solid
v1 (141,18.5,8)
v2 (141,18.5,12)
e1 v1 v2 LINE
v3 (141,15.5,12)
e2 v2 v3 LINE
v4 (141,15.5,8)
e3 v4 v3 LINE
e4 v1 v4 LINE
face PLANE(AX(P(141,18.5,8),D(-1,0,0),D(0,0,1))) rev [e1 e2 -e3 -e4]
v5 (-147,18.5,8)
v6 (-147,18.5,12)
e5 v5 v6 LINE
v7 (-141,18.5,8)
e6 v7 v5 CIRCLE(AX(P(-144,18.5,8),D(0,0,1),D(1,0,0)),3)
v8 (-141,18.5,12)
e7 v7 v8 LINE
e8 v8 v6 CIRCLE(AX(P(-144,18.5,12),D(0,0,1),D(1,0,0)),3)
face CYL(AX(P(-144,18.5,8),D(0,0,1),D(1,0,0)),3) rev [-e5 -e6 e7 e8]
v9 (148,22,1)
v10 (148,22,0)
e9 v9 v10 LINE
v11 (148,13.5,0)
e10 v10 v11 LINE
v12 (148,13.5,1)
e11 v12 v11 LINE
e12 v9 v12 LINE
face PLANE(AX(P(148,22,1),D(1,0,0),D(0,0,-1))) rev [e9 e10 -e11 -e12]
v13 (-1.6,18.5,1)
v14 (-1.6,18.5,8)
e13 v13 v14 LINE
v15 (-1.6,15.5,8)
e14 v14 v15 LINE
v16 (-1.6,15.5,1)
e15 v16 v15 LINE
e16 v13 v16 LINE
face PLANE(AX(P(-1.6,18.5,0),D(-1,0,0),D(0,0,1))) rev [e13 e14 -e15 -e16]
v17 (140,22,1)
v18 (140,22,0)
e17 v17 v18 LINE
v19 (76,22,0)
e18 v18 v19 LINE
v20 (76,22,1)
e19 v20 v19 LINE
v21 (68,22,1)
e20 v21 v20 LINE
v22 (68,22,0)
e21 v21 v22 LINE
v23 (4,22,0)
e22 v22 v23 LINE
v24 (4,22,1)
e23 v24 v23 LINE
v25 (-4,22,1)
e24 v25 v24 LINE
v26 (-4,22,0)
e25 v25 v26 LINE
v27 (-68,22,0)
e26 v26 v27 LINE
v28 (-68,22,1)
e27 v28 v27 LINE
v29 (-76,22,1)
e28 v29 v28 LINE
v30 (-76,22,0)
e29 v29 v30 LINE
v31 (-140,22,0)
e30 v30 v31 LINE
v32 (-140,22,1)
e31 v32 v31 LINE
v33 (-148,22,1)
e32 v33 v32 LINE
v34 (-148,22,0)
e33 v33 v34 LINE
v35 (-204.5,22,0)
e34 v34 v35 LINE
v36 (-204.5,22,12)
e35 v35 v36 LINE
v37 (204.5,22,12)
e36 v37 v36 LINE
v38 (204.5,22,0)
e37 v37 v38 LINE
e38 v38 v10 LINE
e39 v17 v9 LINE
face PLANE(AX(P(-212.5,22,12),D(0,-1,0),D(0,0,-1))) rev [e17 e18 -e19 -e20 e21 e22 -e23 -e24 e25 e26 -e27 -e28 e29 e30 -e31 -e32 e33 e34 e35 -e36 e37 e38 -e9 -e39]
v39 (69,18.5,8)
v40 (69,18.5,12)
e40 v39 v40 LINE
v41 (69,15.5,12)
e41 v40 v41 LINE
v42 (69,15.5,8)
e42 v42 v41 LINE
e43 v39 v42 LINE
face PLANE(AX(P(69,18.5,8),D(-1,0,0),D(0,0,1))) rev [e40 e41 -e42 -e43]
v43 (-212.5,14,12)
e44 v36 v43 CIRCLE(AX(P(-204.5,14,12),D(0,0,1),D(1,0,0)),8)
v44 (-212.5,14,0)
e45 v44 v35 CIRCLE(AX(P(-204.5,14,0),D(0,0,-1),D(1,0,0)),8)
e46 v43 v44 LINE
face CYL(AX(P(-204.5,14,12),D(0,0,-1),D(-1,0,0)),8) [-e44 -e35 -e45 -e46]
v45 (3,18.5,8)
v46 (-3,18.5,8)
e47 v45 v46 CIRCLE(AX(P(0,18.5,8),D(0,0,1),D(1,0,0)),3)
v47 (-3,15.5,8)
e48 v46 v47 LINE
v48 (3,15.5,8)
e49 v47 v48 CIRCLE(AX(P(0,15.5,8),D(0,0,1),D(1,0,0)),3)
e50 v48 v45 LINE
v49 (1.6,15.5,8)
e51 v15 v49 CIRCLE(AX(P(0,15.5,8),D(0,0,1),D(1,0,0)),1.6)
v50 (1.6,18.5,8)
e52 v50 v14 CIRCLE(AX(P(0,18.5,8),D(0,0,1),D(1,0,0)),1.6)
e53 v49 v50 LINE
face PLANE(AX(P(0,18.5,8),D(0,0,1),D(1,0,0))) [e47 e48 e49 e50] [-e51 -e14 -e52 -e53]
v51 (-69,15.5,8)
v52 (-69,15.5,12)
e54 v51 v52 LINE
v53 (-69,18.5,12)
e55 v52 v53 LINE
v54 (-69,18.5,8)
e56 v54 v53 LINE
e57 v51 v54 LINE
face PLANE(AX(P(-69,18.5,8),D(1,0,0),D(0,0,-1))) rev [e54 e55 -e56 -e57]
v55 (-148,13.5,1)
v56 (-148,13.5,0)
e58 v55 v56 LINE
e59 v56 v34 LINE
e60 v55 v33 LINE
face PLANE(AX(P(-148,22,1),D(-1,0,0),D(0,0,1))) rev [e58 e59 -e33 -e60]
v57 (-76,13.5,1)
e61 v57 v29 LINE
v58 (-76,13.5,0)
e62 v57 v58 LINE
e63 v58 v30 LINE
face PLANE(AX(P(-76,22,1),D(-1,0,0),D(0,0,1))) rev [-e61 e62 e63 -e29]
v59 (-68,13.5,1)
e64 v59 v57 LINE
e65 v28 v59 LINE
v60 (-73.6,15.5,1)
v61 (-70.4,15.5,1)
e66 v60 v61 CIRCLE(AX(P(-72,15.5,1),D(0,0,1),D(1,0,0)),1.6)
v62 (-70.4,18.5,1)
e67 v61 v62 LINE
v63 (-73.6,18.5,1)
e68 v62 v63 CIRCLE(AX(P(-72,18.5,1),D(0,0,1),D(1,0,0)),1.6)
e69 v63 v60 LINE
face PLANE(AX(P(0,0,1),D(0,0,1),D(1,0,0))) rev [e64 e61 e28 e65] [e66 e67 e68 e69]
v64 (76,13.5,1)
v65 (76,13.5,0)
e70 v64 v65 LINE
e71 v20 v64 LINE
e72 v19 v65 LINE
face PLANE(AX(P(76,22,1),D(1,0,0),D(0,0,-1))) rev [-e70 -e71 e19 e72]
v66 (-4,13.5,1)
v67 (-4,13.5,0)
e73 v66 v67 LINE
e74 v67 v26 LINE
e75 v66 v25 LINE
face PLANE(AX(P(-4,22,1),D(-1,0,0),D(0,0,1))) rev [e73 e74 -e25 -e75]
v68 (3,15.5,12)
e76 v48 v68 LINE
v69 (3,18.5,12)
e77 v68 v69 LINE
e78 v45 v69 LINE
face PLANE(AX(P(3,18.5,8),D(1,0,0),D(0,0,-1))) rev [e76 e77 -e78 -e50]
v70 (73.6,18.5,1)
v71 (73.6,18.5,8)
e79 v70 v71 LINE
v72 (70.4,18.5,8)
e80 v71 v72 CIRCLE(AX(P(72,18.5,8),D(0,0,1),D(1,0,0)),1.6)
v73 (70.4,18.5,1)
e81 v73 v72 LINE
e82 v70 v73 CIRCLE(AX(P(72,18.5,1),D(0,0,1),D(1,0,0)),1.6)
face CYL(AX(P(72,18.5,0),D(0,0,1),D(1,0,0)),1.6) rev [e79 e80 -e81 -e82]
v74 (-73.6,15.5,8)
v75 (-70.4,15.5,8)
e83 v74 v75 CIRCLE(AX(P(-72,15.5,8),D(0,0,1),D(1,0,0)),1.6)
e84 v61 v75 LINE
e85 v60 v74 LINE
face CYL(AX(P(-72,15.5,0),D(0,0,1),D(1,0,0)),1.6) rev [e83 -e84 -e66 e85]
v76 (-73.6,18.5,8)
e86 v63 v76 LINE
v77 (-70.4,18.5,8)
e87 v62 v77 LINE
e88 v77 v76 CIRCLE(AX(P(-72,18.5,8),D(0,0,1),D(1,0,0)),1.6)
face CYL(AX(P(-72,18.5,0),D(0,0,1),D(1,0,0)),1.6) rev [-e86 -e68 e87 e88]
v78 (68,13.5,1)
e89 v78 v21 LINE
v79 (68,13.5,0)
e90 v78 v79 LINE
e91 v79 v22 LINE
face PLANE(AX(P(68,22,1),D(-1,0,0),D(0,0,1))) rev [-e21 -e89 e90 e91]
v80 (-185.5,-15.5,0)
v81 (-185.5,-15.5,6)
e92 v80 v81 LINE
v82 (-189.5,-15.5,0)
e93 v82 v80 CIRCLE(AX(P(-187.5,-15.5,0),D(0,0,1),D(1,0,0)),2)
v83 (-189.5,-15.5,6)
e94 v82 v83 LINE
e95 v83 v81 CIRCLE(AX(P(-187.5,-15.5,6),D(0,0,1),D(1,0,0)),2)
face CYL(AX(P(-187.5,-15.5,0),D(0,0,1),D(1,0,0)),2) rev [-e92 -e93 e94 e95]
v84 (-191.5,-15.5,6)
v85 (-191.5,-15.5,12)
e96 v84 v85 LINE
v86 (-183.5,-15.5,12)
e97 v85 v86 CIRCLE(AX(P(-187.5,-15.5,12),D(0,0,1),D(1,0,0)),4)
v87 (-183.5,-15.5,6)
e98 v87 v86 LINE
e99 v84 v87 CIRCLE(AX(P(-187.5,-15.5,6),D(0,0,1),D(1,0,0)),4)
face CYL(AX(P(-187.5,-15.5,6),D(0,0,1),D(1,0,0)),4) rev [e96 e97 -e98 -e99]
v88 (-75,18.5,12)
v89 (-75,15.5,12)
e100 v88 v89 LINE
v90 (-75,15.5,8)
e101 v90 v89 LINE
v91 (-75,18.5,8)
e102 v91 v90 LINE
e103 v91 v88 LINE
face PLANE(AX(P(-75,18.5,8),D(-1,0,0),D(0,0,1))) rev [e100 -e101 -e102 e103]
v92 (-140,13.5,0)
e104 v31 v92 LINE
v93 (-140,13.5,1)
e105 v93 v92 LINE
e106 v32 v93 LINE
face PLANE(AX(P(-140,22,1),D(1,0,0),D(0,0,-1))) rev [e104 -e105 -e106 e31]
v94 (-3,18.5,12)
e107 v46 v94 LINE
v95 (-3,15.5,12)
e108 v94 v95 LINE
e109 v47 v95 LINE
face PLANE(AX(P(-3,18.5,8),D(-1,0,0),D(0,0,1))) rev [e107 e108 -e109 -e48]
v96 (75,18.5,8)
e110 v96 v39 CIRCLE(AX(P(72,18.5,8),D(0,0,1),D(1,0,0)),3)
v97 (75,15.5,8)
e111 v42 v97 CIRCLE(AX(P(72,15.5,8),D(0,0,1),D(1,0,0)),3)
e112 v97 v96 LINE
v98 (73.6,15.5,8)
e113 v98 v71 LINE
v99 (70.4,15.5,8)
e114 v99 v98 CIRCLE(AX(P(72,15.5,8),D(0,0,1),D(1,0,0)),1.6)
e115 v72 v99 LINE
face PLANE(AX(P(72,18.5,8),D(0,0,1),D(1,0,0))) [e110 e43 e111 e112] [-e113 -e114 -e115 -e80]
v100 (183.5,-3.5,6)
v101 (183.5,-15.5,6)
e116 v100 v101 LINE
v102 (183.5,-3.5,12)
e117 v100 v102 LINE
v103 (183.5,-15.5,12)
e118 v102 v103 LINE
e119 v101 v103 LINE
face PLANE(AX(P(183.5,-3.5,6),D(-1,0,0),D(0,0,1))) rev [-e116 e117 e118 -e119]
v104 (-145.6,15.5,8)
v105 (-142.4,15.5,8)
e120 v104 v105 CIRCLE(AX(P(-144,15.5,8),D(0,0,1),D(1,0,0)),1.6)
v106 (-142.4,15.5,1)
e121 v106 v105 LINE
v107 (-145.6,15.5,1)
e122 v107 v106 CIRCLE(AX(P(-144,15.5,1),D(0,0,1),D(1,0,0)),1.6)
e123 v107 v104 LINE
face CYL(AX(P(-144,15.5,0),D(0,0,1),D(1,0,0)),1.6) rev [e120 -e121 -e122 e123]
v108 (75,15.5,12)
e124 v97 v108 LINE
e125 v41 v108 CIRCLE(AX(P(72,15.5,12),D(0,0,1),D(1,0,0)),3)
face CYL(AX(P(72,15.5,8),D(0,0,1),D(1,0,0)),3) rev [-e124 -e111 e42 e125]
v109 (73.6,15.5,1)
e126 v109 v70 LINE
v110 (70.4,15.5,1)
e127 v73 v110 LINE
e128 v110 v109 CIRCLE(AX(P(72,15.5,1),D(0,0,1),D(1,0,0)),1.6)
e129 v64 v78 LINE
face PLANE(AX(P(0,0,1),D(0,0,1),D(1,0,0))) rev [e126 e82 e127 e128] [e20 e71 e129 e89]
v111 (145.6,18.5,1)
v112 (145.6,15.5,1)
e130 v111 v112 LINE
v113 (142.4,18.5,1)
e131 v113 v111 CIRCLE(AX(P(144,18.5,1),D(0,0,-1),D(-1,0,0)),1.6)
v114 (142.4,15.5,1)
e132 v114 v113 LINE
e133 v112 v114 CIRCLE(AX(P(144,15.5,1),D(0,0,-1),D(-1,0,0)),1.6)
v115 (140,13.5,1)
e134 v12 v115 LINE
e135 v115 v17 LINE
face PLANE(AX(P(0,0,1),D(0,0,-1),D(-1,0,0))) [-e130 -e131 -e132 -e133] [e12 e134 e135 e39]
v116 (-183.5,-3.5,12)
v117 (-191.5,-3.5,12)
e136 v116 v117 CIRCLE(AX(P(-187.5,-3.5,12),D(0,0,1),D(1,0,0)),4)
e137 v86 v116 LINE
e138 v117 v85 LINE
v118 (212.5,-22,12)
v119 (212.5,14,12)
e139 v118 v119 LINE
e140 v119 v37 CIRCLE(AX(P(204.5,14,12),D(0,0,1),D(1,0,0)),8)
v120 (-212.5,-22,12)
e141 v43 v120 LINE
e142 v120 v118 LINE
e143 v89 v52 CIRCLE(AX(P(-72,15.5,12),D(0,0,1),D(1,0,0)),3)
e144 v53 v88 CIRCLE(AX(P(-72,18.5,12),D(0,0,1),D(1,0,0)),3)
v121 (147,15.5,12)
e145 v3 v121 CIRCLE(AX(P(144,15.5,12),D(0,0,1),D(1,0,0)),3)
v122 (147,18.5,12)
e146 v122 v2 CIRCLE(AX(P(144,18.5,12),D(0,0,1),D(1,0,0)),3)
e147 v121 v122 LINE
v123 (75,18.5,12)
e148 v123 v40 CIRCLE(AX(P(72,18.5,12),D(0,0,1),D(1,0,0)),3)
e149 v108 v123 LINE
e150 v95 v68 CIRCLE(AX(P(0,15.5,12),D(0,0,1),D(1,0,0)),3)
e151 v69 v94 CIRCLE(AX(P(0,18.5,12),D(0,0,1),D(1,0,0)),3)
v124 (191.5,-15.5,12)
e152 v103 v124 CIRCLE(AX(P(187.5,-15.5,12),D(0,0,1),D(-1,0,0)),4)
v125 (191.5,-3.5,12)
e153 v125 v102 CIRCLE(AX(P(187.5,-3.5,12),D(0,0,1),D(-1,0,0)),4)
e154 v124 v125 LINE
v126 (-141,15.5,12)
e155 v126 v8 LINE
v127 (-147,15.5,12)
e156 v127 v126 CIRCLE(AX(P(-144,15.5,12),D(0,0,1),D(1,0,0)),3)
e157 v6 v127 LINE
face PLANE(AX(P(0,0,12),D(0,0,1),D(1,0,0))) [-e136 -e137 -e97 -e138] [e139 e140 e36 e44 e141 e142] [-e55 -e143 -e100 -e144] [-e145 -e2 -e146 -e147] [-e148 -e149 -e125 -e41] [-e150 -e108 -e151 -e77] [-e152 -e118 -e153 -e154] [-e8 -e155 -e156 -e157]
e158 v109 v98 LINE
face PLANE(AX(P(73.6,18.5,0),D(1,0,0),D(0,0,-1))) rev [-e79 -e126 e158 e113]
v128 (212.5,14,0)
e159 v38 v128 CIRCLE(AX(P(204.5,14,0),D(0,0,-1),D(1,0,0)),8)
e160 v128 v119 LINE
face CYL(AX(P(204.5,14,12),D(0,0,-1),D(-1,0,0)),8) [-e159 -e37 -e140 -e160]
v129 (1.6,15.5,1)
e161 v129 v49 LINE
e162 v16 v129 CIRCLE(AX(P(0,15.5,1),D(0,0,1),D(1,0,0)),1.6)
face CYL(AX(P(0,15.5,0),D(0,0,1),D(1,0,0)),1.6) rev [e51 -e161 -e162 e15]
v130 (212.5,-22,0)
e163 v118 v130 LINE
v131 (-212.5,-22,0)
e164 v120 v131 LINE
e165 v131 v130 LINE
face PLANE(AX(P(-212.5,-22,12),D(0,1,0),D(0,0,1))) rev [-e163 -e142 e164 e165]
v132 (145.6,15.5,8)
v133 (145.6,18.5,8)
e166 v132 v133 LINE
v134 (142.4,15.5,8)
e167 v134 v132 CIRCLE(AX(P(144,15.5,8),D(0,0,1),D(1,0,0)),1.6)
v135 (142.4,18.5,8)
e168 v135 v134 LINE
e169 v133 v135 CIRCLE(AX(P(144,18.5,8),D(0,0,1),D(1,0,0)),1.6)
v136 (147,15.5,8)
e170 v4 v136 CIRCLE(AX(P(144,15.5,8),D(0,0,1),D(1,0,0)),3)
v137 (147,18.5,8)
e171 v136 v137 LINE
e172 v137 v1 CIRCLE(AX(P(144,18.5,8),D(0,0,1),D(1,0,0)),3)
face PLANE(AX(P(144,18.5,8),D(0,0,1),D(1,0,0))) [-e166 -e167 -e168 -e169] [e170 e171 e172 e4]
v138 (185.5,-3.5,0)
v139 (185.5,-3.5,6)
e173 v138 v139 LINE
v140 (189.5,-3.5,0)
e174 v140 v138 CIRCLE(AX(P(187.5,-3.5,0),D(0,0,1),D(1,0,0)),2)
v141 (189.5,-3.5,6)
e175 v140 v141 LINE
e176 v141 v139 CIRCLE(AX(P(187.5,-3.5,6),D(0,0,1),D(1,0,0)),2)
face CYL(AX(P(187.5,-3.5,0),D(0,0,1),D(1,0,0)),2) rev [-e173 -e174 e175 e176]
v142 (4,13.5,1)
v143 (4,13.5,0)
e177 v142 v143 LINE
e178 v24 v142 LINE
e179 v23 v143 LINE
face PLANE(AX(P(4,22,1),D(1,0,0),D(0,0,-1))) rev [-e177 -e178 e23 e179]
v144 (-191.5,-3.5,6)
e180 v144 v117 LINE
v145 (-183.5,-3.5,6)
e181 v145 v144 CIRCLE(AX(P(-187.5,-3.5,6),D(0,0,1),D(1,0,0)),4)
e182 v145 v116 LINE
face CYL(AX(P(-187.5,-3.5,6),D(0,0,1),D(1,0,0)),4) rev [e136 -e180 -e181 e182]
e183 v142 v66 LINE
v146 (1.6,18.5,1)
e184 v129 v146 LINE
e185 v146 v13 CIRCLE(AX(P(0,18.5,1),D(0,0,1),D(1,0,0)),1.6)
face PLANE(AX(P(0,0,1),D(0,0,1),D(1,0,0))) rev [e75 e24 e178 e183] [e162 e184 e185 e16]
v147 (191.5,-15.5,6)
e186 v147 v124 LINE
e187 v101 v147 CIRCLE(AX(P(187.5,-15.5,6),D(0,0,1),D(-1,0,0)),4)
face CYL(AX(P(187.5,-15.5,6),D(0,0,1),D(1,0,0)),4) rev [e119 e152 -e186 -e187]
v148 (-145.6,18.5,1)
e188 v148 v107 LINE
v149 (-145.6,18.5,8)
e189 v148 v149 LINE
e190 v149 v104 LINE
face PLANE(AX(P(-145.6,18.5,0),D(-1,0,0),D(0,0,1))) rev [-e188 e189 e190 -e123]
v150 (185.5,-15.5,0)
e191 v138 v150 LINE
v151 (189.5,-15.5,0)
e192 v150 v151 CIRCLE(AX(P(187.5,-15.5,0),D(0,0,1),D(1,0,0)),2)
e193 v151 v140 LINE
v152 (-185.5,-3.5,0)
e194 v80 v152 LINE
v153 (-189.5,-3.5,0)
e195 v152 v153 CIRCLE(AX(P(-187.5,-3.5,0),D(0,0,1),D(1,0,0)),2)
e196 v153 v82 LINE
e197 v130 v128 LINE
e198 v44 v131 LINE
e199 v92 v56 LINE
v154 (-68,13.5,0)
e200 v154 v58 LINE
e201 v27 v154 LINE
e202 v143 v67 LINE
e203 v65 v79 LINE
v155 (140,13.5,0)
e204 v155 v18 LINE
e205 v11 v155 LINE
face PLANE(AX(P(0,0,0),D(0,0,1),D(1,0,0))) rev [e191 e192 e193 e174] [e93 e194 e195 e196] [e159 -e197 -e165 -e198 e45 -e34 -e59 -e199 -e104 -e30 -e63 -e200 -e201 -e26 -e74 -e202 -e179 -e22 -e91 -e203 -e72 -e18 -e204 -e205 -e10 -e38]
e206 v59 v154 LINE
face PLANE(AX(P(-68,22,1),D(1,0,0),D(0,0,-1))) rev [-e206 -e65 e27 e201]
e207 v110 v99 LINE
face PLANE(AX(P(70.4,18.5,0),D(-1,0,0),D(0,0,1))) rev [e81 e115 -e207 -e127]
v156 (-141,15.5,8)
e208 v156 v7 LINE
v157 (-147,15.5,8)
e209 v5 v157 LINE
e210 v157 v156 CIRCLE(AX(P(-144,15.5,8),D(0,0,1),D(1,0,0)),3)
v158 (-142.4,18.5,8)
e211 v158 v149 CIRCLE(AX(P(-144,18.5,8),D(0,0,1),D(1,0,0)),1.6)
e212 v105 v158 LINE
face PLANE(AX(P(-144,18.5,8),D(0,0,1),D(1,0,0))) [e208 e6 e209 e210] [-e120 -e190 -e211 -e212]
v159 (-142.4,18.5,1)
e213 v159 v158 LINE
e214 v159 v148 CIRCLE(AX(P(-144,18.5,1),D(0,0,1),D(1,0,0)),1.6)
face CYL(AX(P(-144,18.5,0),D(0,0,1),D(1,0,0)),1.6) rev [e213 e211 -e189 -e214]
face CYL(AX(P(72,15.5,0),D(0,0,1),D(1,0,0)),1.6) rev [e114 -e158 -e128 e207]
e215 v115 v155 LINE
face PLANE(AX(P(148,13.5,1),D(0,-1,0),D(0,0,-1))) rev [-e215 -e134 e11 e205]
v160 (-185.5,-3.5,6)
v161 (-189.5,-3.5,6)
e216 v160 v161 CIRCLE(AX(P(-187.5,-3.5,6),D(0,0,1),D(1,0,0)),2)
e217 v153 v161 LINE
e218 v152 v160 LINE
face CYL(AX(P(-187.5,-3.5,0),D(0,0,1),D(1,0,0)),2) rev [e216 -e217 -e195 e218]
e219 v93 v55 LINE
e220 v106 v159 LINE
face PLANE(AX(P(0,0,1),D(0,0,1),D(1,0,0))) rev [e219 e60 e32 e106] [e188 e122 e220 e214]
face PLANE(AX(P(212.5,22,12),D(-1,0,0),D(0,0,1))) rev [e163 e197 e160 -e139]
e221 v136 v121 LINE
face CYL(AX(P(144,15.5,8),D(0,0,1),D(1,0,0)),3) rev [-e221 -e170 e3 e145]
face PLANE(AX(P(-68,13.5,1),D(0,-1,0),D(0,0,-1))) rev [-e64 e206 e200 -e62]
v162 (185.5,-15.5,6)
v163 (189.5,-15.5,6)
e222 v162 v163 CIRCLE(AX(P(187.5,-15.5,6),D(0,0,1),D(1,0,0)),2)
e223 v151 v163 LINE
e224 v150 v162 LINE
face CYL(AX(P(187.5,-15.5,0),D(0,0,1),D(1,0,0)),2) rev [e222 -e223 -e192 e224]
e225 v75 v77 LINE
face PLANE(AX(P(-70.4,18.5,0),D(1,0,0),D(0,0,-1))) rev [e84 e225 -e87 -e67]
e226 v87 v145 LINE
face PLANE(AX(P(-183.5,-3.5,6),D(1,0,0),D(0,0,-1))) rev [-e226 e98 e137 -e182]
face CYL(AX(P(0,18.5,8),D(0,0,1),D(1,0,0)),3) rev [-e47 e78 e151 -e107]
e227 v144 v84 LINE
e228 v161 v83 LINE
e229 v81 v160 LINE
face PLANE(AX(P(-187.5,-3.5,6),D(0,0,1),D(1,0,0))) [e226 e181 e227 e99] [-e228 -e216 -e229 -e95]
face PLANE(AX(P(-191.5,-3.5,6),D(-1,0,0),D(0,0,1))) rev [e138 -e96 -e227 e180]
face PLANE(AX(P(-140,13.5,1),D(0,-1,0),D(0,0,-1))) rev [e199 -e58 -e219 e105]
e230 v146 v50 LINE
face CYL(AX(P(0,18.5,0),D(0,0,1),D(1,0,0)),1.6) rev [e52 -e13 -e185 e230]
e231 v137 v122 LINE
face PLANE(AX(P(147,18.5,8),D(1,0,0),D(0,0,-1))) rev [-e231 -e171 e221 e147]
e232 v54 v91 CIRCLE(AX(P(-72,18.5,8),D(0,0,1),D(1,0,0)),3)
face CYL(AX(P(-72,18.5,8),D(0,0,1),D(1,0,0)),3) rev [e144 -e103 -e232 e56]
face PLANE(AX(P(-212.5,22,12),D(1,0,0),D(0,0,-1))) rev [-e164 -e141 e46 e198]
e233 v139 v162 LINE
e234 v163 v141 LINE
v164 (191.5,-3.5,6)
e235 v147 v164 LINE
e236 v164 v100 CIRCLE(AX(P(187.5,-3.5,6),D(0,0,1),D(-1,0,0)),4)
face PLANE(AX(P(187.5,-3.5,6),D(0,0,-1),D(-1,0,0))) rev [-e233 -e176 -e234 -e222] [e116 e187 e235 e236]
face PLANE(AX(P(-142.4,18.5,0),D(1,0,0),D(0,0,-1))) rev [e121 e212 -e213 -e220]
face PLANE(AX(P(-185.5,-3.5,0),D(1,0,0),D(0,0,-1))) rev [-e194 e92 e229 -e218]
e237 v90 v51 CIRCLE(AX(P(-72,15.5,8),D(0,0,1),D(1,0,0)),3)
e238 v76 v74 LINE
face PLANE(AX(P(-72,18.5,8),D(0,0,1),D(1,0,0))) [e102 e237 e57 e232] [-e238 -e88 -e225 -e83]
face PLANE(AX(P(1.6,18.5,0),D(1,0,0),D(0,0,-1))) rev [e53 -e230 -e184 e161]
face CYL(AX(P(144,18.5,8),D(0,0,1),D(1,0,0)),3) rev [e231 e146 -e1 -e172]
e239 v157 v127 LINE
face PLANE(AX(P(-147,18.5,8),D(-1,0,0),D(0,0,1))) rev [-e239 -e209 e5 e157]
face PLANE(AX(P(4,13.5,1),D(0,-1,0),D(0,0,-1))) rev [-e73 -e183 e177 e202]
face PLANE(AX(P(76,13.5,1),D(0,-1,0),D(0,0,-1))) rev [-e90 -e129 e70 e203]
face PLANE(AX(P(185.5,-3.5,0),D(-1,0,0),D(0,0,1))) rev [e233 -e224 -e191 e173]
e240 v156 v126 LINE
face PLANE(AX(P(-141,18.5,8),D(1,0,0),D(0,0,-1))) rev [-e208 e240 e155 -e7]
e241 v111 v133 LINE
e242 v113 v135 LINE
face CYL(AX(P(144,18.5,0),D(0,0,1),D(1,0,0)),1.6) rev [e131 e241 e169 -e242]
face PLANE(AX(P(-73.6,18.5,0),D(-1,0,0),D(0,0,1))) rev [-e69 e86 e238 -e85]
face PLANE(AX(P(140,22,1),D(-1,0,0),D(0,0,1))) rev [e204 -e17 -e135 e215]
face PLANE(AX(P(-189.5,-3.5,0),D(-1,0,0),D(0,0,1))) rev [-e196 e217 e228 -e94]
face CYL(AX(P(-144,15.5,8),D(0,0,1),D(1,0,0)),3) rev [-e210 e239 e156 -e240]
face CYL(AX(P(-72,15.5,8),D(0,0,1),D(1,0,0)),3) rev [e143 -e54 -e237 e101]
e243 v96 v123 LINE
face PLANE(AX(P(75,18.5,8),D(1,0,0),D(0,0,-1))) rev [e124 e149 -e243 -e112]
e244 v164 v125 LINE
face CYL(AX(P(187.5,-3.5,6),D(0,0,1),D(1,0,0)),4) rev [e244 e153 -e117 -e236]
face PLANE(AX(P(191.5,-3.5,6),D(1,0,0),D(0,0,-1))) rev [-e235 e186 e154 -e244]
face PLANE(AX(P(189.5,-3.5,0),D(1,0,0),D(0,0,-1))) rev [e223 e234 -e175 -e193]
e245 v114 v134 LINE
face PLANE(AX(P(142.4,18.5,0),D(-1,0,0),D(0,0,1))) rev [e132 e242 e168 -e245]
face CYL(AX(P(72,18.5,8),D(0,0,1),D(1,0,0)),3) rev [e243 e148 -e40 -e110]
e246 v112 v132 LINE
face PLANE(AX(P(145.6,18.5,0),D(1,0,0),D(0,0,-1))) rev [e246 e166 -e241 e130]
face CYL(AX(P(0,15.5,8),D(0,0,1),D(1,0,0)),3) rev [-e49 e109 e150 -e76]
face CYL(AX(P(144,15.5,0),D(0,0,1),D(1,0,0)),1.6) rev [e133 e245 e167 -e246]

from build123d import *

# Parameters (mm, degrees)
SKETCH_1_W             = 425
SKETCH_1_H             = 44
EXTRUDE_1_DEPTH        = 12
FILLET_1_R             = 8
CUT_EXTRUDE_1_DEPTH    = 6
CUT_EXTRUDE_2_DEPTH    = 214.720027138
SKETCH_4_W             = 8
SKETCH_4_H             = 8.5
CUT_EXTRUDE_3_DEPTH    = 1
CUT_EXTRUDE_4_DEPTH    = 4
CUT_EXTRUDE_5_DEPTH    = 214.785523364
PATTERN_LINEAR_1_COUNT = 5
PATTERN_LINEAR_1_PITCH = 72


with BuildPart() as part:
    # 草图1 → 凸台-拉伸1 (new body)
    with BuildSketch(Plane.XY):
        Rectangle(SKETCH_1_W, SKETCH_1_H)
    extrude(amount=EXTRUDE_1_DEPTH)

    # 圆角1
    fillet_1_edges = [part.edges().sort_by_distance(p)[0] for p in [
        (-212.5, 22, 6),
        (212.5, 22, 6),
    ]]
    fillet(fillet_1_edges, radius=FILLET_1_R)

    # 草图2 → 切除-拉伸1 (cut)
    with BuildSketch(Plane.XY.offset(12)):
        with BuildLine():
            Line((-183.5, -3.5), (-183.5, -15.5))
            ThreePointArc((-183.5, -15.5), (-187.5, -19.5), (-191.5, -15.5))
            Line((-191.5, -15.5), (-191.5, -3.5))
            ThreePointArc((-191.5, -3.5), (-187.5, 0.5), (-183.5, -3.5))
        make_face()
        with BuildLine():
            Line((183.5, -3.5), (183.5, -15.5))
            ThreePointArc((183.5, -15.5), (187.5, -19.5), (191.5, -15.5))
            Line((191.5, -15.5), (191.5, -3.5))
            ThreePointArc((191.5, -3.5), (187.5, 0.5), (183.5, -3.5))
        make_face()
    extrude(amount=-CUT_EXTRUDE_1_DEPTH, mode=Mode.SUBTRACT)

    # 草图3 → 切除-拉伸2 (cut, through all)
    with BuildSketch(Plane.XY.offset(6)):
        with BuildLine():
            Line((-185.5, -3.5), (-185.5, -15.5))
            ThreePointArc((-185.5, -15.5), (-187.5, -17.5), (-189.5, -15.5))
            Line((-189.5, -15.5), (-189.5, -3.5))
            ThreePointArc((-189.5, -3.5), (-187.5, -1.5), (-185.5, -3.5))
        make_face()
        with BuildLine():
            Line((189.5, -3.5), (189.5, -15.5))
            ThreePointArc((189.5, -15.5), (187.5, -17.5), (185.5, -15.5))
            Line((185.5, -15.5), (185.5, -3.5))
            ThreePointArc((185.5, -3.5), (187.5, -1.5), (189.5, -3.5))
        make_face()
    extrude(amount=-CUT_EXTRUDE_2_DEPTH, mode=Mode.SUBTRACT)

    # 草图4 → 切除-拉伸3 (cut)
    with BuildSketch(Plane(origin=(0, 0, 0), x_dir=(-1, 0, 0), z_dir=(0, 0, -1))):
        with Locations((-144, 17.75)):
            Rectangle(SKETCH_4_W, SKETCH_4_H)
        with Locations((-72, 17.75)):
            Rectangle(SKETCH_4_W, SKETCH_4_H)
        with Locations((0, 17.75)):
            Rectangle(SKETCH_4_W, SKETCH_4_H)
        with Locations((72, 17.75)):
            Rectangle(SKETCH_4_W, SKETCH_4_H)
        with Locations((144, 17.75)):
            Rectangle(SKETCH_4_W, SKETCH_4_H)
    extrude(amount=-CUT_EXTRUDE_3_DEPTH, mode=Mode.SUBTRACT)

    # 草图5 → 切除-拉伸4 (cut)
    with BuildSketch(Plane.XY.offset(12)):
        with BuildLine():
            Line((-141, 18.5), (-141, 15.5))
            ThreePointArc((-141, 15.5), (-144, 12.5), (-147, 15.5))
            Line((-147, 15.5), (-147, 18.5))
            ThreePointArc((-147, 18.5), (-144, 21.5), (-141, 18.5))
        make_face()
    cut_extrude_4 = extrude(amount=-CUT_EXTRUDE_4_DEPTH, mode=Mode.SUBTRACT)

    # 草图6 → 切除-拉伸5 (cut, through all)
    with BuildSketch(Plane.XY.offset(8)):
        with BuildLine():
            Line((-142.4, 18.5), (-142.4, 15.5))
            ThreePointArc((-142.4, 15.5), (-144, 13.9), (-145.6, 15.5))
            Line((-145.6, 15.5), (-145.6, 18.5))
            ThreePointArc((-145.6, 18.5), (-144, 20.1), (-142.4, 18.5))
        make_face()
    cut_extrude_5 = extrude(amount=-CUT_EXTRUDE_5_DEPTH, mode=Mode.SUBTRACT)

    # 阵列(线性)1: 切除-拉伸4, 切除-拉伸5 ×5
    with Locations(*[(i * PATTERN_LINEAR_1_PITCH, 0, 0) for i in range(1, PATTERN_LINEAR_1_COUNT)]):
        add(cut_extrude_4, mode=Mode.SUBTRACT)
        add(cut_extrude_5, mode=Mode.SUBTRACT)


solid = part.part
